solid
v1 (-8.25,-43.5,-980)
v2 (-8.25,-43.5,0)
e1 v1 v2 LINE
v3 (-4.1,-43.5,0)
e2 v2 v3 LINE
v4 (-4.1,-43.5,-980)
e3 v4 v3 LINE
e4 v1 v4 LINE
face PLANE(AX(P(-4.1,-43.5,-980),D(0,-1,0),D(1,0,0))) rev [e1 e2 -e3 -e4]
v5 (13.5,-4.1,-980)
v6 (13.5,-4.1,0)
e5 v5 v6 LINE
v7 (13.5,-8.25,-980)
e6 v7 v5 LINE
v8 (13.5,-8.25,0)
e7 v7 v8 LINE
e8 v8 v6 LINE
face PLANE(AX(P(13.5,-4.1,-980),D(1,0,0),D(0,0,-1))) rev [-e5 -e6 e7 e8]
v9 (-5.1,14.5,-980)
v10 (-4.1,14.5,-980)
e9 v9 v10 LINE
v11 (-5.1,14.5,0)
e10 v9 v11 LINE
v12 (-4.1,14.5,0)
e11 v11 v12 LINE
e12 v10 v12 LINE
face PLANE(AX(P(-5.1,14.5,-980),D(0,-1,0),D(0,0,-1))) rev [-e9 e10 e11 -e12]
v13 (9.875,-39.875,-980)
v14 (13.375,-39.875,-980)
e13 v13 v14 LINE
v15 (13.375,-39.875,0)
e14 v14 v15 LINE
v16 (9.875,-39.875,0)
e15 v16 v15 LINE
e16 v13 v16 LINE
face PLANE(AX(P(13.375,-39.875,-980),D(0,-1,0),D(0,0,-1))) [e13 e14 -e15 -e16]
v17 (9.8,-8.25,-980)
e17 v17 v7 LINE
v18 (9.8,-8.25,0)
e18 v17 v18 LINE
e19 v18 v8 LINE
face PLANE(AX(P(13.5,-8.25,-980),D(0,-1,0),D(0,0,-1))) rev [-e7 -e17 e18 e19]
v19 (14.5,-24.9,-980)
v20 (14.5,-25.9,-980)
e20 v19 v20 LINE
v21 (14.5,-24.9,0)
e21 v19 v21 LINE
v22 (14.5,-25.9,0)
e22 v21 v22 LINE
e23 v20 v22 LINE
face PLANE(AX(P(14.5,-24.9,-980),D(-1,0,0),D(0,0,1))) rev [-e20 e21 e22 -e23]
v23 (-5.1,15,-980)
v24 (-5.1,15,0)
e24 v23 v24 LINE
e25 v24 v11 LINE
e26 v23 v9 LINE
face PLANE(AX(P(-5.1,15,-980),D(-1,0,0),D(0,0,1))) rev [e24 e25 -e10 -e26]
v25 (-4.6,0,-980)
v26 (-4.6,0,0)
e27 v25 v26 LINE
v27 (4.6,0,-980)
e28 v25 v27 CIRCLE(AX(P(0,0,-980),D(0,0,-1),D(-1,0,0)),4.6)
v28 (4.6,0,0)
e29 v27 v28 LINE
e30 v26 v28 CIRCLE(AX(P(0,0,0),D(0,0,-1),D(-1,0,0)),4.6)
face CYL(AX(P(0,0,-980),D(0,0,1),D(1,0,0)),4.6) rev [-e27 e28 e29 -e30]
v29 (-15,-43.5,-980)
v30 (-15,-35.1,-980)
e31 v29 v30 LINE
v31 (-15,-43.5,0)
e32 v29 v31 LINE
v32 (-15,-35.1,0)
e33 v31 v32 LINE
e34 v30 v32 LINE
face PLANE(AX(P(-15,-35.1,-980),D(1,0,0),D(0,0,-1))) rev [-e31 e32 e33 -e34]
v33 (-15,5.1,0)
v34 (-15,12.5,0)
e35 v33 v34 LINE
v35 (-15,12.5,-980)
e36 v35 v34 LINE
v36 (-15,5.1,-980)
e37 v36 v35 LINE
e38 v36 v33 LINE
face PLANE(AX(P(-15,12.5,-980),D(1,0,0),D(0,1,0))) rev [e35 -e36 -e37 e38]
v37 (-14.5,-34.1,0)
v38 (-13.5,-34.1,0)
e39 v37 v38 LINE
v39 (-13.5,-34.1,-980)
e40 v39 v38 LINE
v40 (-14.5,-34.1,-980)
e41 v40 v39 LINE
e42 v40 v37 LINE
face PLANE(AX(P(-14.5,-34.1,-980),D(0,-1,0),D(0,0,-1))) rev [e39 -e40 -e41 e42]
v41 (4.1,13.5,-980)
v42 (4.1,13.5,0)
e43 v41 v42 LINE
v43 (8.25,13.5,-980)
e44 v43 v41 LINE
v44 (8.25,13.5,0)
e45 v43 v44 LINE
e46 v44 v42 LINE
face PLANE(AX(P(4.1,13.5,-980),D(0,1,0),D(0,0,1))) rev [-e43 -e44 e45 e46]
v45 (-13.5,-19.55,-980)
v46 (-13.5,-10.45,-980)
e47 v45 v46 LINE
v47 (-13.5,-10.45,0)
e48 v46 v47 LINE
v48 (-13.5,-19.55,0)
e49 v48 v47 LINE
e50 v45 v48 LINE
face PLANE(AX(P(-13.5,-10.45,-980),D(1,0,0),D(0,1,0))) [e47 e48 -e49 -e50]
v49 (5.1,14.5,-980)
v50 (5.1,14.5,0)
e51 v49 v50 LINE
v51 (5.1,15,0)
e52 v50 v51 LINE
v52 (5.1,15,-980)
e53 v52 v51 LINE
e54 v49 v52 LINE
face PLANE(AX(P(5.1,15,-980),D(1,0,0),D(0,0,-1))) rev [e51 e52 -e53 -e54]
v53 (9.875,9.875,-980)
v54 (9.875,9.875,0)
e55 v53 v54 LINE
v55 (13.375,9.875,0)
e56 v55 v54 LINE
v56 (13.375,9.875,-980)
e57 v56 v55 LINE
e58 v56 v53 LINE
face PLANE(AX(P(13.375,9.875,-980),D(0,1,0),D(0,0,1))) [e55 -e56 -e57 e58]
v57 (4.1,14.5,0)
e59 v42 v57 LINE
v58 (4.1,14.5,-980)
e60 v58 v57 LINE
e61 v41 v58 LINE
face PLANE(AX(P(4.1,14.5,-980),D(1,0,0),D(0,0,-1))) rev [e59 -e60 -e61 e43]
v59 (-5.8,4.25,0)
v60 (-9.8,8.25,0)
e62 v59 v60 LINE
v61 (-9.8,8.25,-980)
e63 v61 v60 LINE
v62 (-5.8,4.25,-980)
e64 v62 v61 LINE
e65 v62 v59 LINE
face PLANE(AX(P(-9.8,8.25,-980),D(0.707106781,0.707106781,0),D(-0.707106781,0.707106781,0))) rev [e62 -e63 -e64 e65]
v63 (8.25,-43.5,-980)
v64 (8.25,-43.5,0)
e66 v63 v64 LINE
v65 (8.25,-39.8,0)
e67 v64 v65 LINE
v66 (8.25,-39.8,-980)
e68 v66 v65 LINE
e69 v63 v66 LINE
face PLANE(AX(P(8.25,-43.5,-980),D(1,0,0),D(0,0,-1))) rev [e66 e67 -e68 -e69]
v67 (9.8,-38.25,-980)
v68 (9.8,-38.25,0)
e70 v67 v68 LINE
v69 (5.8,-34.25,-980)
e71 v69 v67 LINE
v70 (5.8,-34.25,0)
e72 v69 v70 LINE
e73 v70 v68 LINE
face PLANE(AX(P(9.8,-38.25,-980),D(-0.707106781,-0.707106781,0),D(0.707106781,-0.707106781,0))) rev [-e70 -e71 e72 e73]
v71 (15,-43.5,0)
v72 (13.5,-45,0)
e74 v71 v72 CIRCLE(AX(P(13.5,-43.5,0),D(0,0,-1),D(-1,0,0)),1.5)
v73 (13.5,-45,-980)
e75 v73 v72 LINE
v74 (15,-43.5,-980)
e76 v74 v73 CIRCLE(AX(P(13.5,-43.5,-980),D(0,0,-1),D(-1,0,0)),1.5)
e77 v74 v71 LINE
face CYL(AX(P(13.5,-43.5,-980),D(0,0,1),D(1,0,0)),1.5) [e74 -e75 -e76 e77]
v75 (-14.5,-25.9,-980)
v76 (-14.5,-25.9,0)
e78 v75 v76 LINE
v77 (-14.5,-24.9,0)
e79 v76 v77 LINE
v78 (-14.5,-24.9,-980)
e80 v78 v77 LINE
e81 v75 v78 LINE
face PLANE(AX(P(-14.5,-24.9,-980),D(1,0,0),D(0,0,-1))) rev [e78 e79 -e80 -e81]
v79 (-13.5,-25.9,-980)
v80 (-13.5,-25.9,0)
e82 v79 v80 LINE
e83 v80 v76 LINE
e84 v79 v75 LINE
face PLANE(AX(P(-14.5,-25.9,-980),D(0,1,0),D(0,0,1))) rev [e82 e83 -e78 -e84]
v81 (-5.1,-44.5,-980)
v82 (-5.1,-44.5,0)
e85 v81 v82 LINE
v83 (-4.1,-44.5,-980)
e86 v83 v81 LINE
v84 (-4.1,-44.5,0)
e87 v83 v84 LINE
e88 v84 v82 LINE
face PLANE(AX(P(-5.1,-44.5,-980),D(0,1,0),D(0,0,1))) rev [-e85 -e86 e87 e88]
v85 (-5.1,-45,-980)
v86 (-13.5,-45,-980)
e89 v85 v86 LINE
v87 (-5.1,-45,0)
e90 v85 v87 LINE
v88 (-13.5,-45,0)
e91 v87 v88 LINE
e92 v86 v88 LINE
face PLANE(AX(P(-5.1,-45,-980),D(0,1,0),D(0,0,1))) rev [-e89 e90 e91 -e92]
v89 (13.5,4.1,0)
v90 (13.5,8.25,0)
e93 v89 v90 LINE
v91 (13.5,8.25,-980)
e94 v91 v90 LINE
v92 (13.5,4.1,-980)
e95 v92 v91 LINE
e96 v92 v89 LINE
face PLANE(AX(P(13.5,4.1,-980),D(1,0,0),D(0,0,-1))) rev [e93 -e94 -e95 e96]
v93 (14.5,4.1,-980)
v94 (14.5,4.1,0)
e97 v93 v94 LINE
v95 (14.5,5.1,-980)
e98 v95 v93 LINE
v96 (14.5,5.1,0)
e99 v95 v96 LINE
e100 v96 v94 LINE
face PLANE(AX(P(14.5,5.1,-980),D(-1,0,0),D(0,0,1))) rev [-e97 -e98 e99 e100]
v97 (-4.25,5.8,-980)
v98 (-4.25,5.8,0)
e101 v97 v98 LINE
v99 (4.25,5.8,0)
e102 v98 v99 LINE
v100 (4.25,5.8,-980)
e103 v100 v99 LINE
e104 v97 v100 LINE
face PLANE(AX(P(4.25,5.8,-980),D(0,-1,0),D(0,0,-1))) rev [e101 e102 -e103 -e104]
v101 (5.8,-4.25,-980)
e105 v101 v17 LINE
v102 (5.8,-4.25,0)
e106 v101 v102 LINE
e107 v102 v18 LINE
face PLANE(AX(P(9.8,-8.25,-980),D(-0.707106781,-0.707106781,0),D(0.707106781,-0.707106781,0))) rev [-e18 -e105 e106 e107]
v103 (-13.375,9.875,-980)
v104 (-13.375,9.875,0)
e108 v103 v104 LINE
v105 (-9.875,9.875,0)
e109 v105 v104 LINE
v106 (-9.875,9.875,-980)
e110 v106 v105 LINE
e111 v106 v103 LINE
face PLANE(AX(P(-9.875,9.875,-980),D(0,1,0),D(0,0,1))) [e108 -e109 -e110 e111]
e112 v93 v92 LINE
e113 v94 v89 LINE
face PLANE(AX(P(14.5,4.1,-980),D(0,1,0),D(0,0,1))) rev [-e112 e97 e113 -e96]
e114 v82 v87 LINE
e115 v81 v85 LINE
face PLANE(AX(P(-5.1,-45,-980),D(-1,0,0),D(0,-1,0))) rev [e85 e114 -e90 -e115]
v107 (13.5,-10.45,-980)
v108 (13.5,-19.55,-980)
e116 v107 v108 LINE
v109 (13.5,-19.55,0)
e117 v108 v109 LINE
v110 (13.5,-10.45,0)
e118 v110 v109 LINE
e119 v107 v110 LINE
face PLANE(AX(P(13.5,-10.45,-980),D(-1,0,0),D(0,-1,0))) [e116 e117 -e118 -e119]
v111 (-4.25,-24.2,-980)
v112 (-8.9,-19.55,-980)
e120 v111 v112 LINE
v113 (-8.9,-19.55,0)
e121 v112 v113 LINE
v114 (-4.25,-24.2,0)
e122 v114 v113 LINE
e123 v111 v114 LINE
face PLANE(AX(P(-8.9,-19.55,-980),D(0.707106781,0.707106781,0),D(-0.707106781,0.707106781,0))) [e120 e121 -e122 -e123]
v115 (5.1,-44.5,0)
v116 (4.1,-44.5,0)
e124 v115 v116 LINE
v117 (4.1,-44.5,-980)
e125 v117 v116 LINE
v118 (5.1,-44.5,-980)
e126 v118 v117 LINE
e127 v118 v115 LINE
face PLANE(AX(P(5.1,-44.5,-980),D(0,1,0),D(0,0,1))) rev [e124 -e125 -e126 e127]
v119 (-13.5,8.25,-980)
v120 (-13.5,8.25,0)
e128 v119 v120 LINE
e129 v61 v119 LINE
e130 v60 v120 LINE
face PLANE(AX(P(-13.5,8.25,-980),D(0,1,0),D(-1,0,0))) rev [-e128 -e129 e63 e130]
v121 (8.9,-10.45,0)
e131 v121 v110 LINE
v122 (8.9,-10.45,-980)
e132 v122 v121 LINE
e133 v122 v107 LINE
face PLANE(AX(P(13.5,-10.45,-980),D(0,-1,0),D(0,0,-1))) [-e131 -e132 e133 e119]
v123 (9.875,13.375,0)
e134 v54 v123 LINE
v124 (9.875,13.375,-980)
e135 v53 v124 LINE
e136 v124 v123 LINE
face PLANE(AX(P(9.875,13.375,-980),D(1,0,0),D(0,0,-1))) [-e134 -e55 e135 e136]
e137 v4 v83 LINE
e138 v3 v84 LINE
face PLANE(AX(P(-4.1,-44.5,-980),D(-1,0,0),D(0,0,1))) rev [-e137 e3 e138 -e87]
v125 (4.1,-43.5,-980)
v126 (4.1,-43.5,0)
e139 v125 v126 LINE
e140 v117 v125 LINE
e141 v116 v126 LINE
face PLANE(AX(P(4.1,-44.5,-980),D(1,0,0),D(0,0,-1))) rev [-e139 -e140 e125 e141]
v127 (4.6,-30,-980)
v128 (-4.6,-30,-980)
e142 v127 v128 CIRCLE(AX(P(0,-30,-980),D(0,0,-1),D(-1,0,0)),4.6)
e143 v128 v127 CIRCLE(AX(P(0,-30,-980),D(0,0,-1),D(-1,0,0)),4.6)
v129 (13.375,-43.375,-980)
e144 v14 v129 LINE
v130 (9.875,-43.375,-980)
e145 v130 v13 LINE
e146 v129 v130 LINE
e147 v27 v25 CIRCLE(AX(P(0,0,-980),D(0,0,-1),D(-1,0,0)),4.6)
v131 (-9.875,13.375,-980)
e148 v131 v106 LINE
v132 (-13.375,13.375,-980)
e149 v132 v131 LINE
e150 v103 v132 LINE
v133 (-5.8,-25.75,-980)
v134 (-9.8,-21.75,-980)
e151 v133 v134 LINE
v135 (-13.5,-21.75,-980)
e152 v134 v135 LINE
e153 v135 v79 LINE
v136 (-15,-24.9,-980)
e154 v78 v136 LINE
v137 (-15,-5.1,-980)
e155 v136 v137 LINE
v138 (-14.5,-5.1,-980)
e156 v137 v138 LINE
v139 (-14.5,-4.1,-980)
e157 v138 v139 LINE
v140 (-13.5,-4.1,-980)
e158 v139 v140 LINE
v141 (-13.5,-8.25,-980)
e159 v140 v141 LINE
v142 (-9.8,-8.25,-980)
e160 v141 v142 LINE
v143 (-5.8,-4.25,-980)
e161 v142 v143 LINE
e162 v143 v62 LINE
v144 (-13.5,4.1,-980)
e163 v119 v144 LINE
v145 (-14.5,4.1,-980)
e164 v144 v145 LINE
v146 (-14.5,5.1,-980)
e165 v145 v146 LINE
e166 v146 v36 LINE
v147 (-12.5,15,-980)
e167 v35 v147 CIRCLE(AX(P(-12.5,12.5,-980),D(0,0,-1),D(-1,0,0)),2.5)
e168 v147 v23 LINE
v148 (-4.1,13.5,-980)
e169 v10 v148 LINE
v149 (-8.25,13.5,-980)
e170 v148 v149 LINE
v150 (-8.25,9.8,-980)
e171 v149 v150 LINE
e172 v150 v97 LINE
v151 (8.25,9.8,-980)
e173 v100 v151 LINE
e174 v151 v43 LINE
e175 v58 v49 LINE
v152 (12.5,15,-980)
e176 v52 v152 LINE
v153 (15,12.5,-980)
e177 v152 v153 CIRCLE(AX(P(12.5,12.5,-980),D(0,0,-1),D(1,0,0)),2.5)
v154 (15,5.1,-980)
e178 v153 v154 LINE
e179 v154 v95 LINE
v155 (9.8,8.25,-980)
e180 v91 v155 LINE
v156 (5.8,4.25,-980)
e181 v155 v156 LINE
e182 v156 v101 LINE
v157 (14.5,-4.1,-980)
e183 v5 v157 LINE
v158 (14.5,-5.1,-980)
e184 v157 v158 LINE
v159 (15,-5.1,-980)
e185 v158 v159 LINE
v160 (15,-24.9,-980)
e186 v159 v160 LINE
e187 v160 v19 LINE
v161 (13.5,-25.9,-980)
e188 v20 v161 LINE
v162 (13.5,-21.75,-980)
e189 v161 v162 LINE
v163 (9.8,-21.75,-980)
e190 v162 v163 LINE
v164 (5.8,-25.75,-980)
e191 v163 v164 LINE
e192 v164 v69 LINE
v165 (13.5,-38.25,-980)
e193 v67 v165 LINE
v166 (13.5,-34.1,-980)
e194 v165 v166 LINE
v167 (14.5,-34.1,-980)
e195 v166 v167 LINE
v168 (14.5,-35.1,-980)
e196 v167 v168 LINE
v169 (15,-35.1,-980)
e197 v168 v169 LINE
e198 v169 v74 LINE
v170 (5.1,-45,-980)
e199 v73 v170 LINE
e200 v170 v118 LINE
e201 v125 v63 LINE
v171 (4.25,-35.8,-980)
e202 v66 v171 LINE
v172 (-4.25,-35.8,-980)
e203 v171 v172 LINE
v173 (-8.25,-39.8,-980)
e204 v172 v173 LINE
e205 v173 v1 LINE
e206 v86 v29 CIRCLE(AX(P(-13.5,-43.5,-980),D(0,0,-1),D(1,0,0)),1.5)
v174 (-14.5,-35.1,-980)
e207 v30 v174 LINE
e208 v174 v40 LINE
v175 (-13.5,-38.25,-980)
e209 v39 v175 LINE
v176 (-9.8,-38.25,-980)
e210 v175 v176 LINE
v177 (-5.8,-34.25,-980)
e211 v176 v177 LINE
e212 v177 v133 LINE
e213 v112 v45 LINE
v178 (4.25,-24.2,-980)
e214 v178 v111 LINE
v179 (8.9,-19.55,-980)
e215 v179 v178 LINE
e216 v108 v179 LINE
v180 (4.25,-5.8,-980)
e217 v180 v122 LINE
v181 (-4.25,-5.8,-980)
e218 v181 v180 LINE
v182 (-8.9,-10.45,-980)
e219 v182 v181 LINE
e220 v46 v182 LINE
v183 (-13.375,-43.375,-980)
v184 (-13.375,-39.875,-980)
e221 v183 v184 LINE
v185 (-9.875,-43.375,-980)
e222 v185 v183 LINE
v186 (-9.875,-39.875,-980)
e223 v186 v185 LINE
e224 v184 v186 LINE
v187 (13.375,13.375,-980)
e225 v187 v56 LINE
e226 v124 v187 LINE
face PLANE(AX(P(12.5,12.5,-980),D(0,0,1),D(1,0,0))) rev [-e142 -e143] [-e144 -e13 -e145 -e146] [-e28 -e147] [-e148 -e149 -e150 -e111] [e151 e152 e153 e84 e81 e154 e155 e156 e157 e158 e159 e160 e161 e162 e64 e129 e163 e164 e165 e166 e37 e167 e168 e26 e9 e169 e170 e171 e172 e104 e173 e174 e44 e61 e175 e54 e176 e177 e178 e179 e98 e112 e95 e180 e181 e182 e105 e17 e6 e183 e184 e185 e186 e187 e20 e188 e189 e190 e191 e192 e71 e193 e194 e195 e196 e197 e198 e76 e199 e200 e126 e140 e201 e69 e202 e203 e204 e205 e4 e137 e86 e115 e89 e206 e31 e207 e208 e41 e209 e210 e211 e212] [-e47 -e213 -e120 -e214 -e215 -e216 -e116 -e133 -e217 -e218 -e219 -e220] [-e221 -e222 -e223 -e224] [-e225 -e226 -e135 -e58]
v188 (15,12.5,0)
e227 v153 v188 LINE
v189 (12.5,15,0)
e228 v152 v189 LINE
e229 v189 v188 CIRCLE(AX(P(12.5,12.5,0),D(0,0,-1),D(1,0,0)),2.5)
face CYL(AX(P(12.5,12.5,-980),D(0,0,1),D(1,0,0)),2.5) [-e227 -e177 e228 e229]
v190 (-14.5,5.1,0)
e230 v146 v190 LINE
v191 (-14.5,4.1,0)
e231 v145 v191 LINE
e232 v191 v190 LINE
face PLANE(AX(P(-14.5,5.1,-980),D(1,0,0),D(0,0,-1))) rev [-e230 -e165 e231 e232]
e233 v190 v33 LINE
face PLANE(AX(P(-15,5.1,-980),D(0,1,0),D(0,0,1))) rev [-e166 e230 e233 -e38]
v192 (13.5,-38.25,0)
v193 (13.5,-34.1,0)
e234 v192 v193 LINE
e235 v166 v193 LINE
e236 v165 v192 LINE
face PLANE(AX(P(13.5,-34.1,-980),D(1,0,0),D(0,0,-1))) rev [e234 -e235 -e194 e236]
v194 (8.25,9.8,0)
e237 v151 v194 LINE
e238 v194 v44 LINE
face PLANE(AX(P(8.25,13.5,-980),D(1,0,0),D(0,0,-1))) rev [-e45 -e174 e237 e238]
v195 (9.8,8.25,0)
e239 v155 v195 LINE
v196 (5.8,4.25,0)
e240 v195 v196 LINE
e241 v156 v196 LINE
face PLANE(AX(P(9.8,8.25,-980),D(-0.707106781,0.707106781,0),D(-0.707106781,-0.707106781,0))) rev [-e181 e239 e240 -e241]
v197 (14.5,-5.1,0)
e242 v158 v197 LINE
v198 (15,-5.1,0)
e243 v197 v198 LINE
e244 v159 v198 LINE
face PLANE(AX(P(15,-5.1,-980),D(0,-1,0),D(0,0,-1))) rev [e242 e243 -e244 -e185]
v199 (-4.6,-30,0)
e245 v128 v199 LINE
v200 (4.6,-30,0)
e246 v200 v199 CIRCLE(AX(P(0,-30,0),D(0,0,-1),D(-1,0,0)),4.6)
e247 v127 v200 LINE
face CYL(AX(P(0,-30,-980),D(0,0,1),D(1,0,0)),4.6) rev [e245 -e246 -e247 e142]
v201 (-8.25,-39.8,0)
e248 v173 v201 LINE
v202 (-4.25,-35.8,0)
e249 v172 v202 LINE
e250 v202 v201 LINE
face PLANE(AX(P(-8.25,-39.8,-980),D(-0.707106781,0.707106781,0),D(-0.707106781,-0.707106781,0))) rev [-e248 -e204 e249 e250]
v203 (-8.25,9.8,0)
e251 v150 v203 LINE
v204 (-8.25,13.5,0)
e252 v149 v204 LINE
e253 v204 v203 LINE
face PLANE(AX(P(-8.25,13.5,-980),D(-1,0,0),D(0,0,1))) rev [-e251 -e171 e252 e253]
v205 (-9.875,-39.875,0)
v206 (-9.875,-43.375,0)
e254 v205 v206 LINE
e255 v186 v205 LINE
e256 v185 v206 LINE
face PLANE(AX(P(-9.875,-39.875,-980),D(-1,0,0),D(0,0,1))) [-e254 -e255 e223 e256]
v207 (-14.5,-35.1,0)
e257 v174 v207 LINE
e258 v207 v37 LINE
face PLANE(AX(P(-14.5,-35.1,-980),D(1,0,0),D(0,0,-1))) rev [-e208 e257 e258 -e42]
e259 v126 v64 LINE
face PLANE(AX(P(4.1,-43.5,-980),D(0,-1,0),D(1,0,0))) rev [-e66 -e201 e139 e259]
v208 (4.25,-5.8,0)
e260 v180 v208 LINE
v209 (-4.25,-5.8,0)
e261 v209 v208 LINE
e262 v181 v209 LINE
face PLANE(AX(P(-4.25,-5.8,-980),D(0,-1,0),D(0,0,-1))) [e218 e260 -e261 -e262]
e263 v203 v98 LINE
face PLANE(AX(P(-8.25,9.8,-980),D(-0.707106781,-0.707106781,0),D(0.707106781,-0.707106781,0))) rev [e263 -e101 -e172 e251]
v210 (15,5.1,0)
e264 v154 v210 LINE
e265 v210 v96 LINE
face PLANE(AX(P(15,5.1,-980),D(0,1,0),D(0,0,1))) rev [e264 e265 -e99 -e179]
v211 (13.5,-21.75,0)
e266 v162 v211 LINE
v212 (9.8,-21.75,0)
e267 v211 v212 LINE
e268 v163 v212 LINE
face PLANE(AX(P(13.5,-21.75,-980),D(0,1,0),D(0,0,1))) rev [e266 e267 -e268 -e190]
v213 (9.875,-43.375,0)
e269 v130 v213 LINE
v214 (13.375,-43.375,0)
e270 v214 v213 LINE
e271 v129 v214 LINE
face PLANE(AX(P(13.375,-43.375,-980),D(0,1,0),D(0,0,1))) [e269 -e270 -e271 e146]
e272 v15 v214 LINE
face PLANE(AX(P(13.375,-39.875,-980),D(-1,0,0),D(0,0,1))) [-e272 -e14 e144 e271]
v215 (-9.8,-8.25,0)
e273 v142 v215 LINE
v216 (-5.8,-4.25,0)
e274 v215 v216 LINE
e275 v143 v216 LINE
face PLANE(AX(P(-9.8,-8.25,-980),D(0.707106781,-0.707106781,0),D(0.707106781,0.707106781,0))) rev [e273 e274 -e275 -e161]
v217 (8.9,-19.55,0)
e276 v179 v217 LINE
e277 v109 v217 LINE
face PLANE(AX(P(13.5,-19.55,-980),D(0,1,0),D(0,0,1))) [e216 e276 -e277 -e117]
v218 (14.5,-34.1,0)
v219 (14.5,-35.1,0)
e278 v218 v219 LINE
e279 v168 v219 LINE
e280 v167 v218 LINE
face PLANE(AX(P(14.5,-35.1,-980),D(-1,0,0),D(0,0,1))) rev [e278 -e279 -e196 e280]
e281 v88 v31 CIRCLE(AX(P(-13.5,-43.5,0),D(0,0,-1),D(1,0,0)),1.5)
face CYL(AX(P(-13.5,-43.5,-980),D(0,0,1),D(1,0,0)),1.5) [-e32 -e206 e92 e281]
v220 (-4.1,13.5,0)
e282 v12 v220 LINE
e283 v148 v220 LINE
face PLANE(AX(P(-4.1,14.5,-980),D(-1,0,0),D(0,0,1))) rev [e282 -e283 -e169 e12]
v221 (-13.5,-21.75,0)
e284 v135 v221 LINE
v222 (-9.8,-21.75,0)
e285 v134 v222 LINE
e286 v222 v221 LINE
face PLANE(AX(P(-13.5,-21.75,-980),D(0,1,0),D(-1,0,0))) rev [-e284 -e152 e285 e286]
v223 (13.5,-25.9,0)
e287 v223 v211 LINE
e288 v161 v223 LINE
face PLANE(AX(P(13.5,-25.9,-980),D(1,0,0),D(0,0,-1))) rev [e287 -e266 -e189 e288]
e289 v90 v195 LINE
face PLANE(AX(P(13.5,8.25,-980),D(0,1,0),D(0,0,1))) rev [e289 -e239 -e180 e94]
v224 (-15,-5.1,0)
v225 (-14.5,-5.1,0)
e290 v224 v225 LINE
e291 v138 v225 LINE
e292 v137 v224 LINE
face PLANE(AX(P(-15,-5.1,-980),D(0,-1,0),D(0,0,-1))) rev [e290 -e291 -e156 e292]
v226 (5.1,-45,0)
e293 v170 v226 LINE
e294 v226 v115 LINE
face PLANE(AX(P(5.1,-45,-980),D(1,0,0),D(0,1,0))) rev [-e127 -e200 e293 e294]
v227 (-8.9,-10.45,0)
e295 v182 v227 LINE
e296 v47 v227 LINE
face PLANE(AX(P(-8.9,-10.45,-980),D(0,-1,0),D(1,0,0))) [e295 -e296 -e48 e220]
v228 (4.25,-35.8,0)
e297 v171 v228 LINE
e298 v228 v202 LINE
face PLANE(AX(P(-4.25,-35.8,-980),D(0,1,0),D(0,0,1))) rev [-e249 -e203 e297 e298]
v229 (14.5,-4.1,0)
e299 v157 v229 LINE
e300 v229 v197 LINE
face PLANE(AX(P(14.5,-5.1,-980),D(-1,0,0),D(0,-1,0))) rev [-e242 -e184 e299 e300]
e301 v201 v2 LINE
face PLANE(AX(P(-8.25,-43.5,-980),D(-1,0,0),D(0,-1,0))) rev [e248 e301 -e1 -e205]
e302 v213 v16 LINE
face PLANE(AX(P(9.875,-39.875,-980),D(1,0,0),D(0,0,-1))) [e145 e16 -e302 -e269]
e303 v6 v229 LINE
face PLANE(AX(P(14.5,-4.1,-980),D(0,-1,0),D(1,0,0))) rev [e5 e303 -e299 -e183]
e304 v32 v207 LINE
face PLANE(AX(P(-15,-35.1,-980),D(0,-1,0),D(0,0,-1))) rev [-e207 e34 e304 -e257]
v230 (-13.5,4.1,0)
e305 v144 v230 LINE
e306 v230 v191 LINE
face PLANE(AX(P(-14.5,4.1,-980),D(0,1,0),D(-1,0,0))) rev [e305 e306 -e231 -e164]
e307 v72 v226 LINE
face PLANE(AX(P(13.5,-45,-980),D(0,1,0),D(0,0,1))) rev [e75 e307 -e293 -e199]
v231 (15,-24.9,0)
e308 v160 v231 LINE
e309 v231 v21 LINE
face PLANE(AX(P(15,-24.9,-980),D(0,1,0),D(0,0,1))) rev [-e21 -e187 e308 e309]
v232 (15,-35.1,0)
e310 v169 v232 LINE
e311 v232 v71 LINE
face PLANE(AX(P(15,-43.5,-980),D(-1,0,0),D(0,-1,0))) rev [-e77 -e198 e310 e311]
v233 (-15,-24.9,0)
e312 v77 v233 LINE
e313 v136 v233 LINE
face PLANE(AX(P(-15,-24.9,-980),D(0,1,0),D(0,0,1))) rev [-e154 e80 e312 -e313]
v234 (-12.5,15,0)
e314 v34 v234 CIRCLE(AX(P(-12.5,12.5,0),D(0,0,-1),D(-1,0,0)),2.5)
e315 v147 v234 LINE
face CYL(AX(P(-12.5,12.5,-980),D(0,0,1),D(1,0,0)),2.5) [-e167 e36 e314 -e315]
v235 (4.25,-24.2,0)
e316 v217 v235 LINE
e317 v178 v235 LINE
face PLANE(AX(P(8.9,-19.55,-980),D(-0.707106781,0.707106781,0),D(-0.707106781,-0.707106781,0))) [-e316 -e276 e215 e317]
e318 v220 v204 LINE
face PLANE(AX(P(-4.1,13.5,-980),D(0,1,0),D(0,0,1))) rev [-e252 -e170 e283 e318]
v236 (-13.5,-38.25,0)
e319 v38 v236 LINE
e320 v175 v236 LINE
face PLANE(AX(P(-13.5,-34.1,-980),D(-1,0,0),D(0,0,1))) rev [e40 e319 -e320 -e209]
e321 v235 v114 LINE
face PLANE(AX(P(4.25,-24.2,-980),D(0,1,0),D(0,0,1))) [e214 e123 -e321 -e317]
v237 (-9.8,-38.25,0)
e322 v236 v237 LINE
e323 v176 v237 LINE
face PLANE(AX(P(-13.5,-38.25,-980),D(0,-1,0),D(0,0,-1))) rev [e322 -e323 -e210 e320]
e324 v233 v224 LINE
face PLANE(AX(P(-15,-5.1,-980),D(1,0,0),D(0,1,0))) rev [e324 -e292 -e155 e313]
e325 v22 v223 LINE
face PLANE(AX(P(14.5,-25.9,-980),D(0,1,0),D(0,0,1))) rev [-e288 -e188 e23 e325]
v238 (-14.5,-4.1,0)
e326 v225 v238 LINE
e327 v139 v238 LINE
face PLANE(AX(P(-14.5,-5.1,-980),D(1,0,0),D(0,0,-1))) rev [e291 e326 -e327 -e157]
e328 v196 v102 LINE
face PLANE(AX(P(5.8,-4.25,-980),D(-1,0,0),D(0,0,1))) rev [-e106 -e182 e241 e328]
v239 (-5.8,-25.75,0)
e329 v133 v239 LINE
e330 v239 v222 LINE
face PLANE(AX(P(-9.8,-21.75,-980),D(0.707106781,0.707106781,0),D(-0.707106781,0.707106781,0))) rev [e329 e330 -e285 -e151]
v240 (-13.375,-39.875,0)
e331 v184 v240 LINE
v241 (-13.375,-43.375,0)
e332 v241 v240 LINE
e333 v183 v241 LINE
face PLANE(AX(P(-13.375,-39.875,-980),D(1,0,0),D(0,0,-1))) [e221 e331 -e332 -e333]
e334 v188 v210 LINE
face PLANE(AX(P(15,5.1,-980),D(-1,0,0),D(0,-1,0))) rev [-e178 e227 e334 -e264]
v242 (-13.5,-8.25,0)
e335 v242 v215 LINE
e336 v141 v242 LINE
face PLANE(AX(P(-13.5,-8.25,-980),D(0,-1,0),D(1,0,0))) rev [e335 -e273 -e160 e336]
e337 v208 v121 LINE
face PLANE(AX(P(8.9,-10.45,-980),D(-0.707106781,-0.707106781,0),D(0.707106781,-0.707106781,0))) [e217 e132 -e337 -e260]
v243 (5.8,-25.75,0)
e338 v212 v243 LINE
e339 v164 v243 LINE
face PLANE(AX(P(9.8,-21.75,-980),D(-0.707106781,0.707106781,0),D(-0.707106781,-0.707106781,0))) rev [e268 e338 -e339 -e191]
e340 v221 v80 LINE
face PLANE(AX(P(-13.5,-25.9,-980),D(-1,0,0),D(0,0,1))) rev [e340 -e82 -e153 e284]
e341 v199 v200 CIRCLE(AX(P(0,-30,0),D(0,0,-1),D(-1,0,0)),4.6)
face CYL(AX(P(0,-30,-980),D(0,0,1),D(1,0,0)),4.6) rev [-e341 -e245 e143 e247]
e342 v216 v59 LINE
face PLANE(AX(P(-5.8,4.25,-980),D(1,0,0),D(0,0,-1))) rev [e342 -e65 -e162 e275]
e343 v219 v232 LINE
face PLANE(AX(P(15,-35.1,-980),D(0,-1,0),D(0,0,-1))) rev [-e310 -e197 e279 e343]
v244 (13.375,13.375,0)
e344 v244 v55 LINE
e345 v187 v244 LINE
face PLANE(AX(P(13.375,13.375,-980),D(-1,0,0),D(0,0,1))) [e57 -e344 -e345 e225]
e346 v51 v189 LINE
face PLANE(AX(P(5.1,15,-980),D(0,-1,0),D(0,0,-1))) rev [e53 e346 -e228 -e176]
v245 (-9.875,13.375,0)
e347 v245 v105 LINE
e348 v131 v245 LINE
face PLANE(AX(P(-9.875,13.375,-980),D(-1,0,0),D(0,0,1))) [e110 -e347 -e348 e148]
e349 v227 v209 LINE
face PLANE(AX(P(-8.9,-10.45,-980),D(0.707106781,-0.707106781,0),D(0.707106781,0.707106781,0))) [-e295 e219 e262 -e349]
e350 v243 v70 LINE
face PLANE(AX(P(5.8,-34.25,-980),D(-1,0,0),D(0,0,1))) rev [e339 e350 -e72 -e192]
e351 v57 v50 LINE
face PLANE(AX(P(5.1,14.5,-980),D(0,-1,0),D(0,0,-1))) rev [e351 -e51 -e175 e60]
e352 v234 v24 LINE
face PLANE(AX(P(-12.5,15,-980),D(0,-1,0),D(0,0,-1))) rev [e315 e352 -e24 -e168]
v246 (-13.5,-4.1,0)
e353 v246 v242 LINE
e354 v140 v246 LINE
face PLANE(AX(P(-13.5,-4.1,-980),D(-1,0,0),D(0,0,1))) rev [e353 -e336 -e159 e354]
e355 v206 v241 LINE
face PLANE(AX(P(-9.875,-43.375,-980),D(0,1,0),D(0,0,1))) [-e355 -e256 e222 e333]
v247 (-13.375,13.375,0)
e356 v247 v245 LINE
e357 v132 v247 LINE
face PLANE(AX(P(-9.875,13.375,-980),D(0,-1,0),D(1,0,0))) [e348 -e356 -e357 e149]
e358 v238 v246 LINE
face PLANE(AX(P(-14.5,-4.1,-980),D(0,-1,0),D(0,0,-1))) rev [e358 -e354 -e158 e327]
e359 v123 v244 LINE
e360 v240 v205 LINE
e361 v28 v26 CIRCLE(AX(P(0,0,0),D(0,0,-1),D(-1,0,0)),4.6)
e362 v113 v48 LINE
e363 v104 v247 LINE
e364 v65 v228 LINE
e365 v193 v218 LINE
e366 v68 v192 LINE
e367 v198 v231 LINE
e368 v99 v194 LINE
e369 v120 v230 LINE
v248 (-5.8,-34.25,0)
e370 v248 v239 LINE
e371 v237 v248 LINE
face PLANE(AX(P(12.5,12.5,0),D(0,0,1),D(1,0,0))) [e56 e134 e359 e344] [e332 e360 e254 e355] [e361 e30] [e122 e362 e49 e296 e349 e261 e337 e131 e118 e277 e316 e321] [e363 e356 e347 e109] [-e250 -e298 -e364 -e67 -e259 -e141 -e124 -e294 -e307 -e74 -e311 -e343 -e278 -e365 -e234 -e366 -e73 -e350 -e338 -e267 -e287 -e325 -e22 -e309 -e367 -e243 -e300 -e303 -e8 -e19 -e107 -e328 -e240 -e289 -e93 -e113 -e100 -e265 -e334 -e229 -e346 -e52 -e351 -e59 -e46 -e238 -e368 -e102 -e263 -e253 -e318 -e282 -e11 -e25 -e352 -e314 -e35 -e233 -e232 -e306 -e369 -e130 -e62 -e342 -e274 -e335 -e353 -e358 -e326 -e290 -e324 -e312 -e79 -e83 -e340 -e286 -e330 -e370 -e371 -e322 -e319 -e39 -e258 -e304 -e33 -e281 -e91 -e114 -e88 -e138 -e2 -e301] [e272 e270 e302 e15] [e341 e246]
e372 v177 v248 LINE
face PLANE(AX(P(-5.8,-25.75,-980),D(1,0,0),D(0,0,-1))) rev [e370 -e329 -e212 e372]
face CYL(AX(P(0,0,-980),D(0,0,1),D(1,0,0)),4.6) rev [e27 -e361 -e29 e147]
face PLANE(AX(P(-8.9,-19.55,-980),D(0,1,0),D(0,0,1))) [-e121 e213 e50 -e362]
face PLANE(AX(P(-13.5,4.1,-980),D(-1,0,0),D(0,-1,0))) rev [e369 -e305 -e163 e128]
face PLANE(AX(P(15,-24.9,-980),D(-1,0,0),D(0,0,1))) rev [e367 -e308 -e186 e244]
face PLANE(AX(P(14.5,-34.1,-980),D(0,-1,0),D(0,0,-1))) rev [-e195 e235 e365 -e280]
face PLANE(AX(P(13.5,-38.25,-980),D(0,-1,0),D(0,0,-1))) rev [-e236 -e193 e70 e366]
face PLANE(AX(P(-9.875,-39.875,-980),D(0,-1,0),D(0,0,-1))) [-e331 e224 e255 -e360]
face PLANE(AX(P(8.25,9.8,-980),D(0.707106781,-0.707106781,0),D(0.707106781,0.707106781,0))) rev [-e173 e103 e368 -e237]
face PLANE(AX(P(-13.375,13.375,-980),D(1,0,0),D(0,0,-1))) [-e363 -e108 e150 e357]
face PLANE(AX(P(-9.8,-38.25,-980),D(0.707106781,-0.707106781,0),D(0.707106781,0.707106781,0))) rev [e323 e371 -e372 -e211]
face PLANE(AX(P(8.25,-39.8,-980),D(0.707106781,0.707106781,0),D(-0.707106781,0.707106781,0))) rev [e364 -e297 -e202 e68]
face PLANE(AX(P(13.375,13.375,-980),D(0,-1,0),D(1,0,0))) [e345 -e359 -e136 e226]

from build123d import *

# Parameters (mm, degrees)
SKETCH1_R                 = 4.6
SKETCH1_W                 = 3.5
SKETCH1_H                 = 3.5
F_30_X_60L_X_R2_5_1_DEPTH = 980


with BuildPart() as part:
    # Sketch1 → 铝型材 30 X 60L X R2.5(1) (new body)
    with BuildSketch(Plane(origin=(0, 0, 0), x_dir=(-1, 0, 0), z_dir=(0, 0, -1))):
        with BuildLine():
            Line((-5.1, 15), (-5.1, 14.5))
            Line((-5.1, 14.5), (-4.1, 14.5))
            Line((-4.1, 14.5), (-4.1, 13.5))
            Line((-4.1, 13.5), (-8.25, 13.5))
            Line((-8.25, 13.5), (-8.25, 9.8))
            Line((-8.25, 9.8), (-4.25, 5.8))
            Line((-4.25, 5.8), (4.25, 5.8))
            Line((4.25, 5.8), (8.25, 9.8))
            Line((8.25, 9.8), (8.25, 13.5))
            Line((8.25, 13.5), (4.1, 13.5))
            Line((4.1, 13.5), (4.1, 14.5))
            Line((4.1, 14.5), (5.1, 14.5))
            Line((5.1, 14.5), (5.1, 15))
            Line((5.1, 15), (12.5, 15))
            ThreePointArc((12.5, 15), (14.267766953, 14.267766953), (15, 12.5))
            Line((15, 12.5), (15, 5.1))
            Line((15, 5.1), (14.5, 5.1))
            Line((14.5, 5.1), (14.5, 4.1))
            Line((14.5, 4.1), (13.5, 4.1))
            Line((13.5, 4.1), (13.5, 8.25))
            Line((13.5, 8.25), (9.8, 8.25))
            Line((9.8, 8.25), (5.8, 4.25))
            Line((5.8, 4.25), (5.8, -4.25))
            Line((5.8, -4.25), (9.8, -8.25))
            Line((9.8, -8.25), (13.5, -8.25))
            Line((13.5, -8.25), (13.5, -4.1))
            Line((13.5, -4.1), (14.5, -4.1))
            Line((14.5, -4.1), (14.5, -5.1))
            Line((14.5, -5.1), (15, -5.1))
            Line((15, -5.1), (15, -24.9))
            Line((15, -24.9), (14.5, -24.9))
            Line((14.5, -24.9), (14.5, -25.9))
            Line((14.5, -25.9), (13.5, -25.9))
            Line((13.5, -25.9), (13.5, -21.75))
            Line((13.5, -21.75), (9.8, -21.75))
            Line((9.8, -21.75), (5.8, -25.75))
            Line((5.8, -25.75), (5.8, -34.25))
            Line((5.8, -34.25), (9.8, -38.25))
            Line((9.8, -38.25), (13.5, -38.25))
            Line((13.5, -38.25), (13.5, -34.1))
            Line((13.5, -34.1), (14.5, -34.1))
            Line((14.5, -34.1), (14.5, -35.1))
            Line((14.5, -35.1), (15, -35.1))
            Line((15, -35.1), (15, -43.5))
            ThreePointArc((15, -43.5), (14.560660172, -44.560660172), (13.5, -45))
            Line((13.5, -45), (5.1, -45))
            Line((5.1, -45), (5.1, -44.5))
            Line((5.1, -44.5), (4.1, -44.5))
            Line((4.1, -44.5), (4.1, -43.5))
            Line((4.1, -43.5), (8.25, -43.5))
            Line((8.25, -43.5), (8.25, -39.8))
            Line((8.25, -39.8), (4.25, -35.8))
            Line((4.25, -35.8), (-4.25, -35.8))
            Line((-4.25, -35.8), (-8.25, -39.8))
            Line((-8.25, -39.8), (-8.25, -43.5))
            Line((-8.25, -43.5), (-4.1, -43.5))
            Line((-4.1, -43.5), (-4.1, -44.5))
            Line((-4.1, -44.5), (-5.1, -44.5))
            Line((-5.1, -44.5), (-5.1, -45))
            Line((-5.1, -45), (-13.5, -45))
            ThreePointArc((-13.5, -45), (-14.560660172, -44.560660172), (-15, -43.5))
            Line((-15, -43.5), (-15, -35.1))
            Line((-15, -35.1), (-14.5, -35.1))
            Line((-14.5, -35.1), (-14.5, -34.1))
            Line((-14.5, -34.1), (-13.5, -34.1))
            Line((-13.5, -34.1), (-13.5, -38.25))
            Line((-13.5, -38.25), (-9.8, -38.25))
            Line((-9.8, -38.25), (-5.8, -34.25))
            Line((-5.8, -34.25), (-5.8, -25.75))
            Line((-5.8, -25.75), (-9.8, -21.75))
            Line((-9.8, -21.75), (-13.5, -21.75))
            Line((-13.5, -21.75), (-13.5, -25.9))
            Line((-13.5, -25.9), (-14.5, -25.9))
            Line((-14.5, -25.9), (-14.5, -24.9))
            Line((-14.5, -24.9), (-15, -24.9))
            Line((-15, -24.9), (-15, -5.1))
            Line((-15, -5.1), (-14.5, -5.1))
            Line((-14.5, -5.1), (-14.5, -4.1))
            Line((-14.5, -4.1), (-13.5, -4.1))
            Line((-13.5, -4.1), (-13.5, -8.25))
            Line((-13.5, -8.25), (-9.8, -8.25))
            Line((-9.8, -8.25), (-5.8, -4.25))
            Line((-5.8, -4.25), (-5.8, 4.25))
            Line((-5.8, 4.25), (-9.8, 8.25))
            Line((-9.8, 8.25), (-13.5, 8.25))
            Line((-13.5, 8.25), (-13.5, 4.1))
            Line((-13.5, 4.1), (-14.5, 4.1))
            Line((-14.5, 4.1), (-14.5, 5.1))
            Line((-14.5, 5.1), (-15, 5.1))
            Line((-15, 5.1), (-15, 12.5))
            ThreePointArc((-15, 12.5), (-14.267766953, 14.267766953), (-12.5, 15))
            Line((-12.5, 15), (-5.1, 15))
        make_face()
        Circle(SKETCH1_R, mode=Mode.SUBTRACT)
        with Locations((0, -30)):
            Circle(SKETCH1_R, mode=Mode.SUBTRACT)
        Polygon((8.9, -10.45), (4.25, -5.8), (-4.25, -5.8), (-8.9, -10.45), (-13.5, -10.45), (-13.5, -19.55), (-8.9, -19.55), (-4.25, -24.2), (4.25, -24.2), (8.9, -19.55), (13.5, -19.55), (13.5, -10.45), align=None, mode=Mode.SUBTRACT)
        with Locations((-11.625, 11.625)):
            Rectangle(SKETCH1_W, SKETCH1_H, mode=Mode.SUBTRACT)
        with Locations((11.625, 11.625)):
            Rectangle(SKETCH1_W, SKETCH1_H, mode=Mode.SUBTRACT)
        with Locations((-11.625, -41.625)):
            Rectangle(SKETCH1_W, SKETCH1_H, mode=Mode.SUBTRACT)
        with Locations((11.625, -41.625)):
            Rectangle(SKETCH1_W, SKETCH1_H, mode=Mode.SUBTRACT)
    extrude(amount=F_30_X_60L_X_R2_5_1_DEPTH)


solid = part.part
